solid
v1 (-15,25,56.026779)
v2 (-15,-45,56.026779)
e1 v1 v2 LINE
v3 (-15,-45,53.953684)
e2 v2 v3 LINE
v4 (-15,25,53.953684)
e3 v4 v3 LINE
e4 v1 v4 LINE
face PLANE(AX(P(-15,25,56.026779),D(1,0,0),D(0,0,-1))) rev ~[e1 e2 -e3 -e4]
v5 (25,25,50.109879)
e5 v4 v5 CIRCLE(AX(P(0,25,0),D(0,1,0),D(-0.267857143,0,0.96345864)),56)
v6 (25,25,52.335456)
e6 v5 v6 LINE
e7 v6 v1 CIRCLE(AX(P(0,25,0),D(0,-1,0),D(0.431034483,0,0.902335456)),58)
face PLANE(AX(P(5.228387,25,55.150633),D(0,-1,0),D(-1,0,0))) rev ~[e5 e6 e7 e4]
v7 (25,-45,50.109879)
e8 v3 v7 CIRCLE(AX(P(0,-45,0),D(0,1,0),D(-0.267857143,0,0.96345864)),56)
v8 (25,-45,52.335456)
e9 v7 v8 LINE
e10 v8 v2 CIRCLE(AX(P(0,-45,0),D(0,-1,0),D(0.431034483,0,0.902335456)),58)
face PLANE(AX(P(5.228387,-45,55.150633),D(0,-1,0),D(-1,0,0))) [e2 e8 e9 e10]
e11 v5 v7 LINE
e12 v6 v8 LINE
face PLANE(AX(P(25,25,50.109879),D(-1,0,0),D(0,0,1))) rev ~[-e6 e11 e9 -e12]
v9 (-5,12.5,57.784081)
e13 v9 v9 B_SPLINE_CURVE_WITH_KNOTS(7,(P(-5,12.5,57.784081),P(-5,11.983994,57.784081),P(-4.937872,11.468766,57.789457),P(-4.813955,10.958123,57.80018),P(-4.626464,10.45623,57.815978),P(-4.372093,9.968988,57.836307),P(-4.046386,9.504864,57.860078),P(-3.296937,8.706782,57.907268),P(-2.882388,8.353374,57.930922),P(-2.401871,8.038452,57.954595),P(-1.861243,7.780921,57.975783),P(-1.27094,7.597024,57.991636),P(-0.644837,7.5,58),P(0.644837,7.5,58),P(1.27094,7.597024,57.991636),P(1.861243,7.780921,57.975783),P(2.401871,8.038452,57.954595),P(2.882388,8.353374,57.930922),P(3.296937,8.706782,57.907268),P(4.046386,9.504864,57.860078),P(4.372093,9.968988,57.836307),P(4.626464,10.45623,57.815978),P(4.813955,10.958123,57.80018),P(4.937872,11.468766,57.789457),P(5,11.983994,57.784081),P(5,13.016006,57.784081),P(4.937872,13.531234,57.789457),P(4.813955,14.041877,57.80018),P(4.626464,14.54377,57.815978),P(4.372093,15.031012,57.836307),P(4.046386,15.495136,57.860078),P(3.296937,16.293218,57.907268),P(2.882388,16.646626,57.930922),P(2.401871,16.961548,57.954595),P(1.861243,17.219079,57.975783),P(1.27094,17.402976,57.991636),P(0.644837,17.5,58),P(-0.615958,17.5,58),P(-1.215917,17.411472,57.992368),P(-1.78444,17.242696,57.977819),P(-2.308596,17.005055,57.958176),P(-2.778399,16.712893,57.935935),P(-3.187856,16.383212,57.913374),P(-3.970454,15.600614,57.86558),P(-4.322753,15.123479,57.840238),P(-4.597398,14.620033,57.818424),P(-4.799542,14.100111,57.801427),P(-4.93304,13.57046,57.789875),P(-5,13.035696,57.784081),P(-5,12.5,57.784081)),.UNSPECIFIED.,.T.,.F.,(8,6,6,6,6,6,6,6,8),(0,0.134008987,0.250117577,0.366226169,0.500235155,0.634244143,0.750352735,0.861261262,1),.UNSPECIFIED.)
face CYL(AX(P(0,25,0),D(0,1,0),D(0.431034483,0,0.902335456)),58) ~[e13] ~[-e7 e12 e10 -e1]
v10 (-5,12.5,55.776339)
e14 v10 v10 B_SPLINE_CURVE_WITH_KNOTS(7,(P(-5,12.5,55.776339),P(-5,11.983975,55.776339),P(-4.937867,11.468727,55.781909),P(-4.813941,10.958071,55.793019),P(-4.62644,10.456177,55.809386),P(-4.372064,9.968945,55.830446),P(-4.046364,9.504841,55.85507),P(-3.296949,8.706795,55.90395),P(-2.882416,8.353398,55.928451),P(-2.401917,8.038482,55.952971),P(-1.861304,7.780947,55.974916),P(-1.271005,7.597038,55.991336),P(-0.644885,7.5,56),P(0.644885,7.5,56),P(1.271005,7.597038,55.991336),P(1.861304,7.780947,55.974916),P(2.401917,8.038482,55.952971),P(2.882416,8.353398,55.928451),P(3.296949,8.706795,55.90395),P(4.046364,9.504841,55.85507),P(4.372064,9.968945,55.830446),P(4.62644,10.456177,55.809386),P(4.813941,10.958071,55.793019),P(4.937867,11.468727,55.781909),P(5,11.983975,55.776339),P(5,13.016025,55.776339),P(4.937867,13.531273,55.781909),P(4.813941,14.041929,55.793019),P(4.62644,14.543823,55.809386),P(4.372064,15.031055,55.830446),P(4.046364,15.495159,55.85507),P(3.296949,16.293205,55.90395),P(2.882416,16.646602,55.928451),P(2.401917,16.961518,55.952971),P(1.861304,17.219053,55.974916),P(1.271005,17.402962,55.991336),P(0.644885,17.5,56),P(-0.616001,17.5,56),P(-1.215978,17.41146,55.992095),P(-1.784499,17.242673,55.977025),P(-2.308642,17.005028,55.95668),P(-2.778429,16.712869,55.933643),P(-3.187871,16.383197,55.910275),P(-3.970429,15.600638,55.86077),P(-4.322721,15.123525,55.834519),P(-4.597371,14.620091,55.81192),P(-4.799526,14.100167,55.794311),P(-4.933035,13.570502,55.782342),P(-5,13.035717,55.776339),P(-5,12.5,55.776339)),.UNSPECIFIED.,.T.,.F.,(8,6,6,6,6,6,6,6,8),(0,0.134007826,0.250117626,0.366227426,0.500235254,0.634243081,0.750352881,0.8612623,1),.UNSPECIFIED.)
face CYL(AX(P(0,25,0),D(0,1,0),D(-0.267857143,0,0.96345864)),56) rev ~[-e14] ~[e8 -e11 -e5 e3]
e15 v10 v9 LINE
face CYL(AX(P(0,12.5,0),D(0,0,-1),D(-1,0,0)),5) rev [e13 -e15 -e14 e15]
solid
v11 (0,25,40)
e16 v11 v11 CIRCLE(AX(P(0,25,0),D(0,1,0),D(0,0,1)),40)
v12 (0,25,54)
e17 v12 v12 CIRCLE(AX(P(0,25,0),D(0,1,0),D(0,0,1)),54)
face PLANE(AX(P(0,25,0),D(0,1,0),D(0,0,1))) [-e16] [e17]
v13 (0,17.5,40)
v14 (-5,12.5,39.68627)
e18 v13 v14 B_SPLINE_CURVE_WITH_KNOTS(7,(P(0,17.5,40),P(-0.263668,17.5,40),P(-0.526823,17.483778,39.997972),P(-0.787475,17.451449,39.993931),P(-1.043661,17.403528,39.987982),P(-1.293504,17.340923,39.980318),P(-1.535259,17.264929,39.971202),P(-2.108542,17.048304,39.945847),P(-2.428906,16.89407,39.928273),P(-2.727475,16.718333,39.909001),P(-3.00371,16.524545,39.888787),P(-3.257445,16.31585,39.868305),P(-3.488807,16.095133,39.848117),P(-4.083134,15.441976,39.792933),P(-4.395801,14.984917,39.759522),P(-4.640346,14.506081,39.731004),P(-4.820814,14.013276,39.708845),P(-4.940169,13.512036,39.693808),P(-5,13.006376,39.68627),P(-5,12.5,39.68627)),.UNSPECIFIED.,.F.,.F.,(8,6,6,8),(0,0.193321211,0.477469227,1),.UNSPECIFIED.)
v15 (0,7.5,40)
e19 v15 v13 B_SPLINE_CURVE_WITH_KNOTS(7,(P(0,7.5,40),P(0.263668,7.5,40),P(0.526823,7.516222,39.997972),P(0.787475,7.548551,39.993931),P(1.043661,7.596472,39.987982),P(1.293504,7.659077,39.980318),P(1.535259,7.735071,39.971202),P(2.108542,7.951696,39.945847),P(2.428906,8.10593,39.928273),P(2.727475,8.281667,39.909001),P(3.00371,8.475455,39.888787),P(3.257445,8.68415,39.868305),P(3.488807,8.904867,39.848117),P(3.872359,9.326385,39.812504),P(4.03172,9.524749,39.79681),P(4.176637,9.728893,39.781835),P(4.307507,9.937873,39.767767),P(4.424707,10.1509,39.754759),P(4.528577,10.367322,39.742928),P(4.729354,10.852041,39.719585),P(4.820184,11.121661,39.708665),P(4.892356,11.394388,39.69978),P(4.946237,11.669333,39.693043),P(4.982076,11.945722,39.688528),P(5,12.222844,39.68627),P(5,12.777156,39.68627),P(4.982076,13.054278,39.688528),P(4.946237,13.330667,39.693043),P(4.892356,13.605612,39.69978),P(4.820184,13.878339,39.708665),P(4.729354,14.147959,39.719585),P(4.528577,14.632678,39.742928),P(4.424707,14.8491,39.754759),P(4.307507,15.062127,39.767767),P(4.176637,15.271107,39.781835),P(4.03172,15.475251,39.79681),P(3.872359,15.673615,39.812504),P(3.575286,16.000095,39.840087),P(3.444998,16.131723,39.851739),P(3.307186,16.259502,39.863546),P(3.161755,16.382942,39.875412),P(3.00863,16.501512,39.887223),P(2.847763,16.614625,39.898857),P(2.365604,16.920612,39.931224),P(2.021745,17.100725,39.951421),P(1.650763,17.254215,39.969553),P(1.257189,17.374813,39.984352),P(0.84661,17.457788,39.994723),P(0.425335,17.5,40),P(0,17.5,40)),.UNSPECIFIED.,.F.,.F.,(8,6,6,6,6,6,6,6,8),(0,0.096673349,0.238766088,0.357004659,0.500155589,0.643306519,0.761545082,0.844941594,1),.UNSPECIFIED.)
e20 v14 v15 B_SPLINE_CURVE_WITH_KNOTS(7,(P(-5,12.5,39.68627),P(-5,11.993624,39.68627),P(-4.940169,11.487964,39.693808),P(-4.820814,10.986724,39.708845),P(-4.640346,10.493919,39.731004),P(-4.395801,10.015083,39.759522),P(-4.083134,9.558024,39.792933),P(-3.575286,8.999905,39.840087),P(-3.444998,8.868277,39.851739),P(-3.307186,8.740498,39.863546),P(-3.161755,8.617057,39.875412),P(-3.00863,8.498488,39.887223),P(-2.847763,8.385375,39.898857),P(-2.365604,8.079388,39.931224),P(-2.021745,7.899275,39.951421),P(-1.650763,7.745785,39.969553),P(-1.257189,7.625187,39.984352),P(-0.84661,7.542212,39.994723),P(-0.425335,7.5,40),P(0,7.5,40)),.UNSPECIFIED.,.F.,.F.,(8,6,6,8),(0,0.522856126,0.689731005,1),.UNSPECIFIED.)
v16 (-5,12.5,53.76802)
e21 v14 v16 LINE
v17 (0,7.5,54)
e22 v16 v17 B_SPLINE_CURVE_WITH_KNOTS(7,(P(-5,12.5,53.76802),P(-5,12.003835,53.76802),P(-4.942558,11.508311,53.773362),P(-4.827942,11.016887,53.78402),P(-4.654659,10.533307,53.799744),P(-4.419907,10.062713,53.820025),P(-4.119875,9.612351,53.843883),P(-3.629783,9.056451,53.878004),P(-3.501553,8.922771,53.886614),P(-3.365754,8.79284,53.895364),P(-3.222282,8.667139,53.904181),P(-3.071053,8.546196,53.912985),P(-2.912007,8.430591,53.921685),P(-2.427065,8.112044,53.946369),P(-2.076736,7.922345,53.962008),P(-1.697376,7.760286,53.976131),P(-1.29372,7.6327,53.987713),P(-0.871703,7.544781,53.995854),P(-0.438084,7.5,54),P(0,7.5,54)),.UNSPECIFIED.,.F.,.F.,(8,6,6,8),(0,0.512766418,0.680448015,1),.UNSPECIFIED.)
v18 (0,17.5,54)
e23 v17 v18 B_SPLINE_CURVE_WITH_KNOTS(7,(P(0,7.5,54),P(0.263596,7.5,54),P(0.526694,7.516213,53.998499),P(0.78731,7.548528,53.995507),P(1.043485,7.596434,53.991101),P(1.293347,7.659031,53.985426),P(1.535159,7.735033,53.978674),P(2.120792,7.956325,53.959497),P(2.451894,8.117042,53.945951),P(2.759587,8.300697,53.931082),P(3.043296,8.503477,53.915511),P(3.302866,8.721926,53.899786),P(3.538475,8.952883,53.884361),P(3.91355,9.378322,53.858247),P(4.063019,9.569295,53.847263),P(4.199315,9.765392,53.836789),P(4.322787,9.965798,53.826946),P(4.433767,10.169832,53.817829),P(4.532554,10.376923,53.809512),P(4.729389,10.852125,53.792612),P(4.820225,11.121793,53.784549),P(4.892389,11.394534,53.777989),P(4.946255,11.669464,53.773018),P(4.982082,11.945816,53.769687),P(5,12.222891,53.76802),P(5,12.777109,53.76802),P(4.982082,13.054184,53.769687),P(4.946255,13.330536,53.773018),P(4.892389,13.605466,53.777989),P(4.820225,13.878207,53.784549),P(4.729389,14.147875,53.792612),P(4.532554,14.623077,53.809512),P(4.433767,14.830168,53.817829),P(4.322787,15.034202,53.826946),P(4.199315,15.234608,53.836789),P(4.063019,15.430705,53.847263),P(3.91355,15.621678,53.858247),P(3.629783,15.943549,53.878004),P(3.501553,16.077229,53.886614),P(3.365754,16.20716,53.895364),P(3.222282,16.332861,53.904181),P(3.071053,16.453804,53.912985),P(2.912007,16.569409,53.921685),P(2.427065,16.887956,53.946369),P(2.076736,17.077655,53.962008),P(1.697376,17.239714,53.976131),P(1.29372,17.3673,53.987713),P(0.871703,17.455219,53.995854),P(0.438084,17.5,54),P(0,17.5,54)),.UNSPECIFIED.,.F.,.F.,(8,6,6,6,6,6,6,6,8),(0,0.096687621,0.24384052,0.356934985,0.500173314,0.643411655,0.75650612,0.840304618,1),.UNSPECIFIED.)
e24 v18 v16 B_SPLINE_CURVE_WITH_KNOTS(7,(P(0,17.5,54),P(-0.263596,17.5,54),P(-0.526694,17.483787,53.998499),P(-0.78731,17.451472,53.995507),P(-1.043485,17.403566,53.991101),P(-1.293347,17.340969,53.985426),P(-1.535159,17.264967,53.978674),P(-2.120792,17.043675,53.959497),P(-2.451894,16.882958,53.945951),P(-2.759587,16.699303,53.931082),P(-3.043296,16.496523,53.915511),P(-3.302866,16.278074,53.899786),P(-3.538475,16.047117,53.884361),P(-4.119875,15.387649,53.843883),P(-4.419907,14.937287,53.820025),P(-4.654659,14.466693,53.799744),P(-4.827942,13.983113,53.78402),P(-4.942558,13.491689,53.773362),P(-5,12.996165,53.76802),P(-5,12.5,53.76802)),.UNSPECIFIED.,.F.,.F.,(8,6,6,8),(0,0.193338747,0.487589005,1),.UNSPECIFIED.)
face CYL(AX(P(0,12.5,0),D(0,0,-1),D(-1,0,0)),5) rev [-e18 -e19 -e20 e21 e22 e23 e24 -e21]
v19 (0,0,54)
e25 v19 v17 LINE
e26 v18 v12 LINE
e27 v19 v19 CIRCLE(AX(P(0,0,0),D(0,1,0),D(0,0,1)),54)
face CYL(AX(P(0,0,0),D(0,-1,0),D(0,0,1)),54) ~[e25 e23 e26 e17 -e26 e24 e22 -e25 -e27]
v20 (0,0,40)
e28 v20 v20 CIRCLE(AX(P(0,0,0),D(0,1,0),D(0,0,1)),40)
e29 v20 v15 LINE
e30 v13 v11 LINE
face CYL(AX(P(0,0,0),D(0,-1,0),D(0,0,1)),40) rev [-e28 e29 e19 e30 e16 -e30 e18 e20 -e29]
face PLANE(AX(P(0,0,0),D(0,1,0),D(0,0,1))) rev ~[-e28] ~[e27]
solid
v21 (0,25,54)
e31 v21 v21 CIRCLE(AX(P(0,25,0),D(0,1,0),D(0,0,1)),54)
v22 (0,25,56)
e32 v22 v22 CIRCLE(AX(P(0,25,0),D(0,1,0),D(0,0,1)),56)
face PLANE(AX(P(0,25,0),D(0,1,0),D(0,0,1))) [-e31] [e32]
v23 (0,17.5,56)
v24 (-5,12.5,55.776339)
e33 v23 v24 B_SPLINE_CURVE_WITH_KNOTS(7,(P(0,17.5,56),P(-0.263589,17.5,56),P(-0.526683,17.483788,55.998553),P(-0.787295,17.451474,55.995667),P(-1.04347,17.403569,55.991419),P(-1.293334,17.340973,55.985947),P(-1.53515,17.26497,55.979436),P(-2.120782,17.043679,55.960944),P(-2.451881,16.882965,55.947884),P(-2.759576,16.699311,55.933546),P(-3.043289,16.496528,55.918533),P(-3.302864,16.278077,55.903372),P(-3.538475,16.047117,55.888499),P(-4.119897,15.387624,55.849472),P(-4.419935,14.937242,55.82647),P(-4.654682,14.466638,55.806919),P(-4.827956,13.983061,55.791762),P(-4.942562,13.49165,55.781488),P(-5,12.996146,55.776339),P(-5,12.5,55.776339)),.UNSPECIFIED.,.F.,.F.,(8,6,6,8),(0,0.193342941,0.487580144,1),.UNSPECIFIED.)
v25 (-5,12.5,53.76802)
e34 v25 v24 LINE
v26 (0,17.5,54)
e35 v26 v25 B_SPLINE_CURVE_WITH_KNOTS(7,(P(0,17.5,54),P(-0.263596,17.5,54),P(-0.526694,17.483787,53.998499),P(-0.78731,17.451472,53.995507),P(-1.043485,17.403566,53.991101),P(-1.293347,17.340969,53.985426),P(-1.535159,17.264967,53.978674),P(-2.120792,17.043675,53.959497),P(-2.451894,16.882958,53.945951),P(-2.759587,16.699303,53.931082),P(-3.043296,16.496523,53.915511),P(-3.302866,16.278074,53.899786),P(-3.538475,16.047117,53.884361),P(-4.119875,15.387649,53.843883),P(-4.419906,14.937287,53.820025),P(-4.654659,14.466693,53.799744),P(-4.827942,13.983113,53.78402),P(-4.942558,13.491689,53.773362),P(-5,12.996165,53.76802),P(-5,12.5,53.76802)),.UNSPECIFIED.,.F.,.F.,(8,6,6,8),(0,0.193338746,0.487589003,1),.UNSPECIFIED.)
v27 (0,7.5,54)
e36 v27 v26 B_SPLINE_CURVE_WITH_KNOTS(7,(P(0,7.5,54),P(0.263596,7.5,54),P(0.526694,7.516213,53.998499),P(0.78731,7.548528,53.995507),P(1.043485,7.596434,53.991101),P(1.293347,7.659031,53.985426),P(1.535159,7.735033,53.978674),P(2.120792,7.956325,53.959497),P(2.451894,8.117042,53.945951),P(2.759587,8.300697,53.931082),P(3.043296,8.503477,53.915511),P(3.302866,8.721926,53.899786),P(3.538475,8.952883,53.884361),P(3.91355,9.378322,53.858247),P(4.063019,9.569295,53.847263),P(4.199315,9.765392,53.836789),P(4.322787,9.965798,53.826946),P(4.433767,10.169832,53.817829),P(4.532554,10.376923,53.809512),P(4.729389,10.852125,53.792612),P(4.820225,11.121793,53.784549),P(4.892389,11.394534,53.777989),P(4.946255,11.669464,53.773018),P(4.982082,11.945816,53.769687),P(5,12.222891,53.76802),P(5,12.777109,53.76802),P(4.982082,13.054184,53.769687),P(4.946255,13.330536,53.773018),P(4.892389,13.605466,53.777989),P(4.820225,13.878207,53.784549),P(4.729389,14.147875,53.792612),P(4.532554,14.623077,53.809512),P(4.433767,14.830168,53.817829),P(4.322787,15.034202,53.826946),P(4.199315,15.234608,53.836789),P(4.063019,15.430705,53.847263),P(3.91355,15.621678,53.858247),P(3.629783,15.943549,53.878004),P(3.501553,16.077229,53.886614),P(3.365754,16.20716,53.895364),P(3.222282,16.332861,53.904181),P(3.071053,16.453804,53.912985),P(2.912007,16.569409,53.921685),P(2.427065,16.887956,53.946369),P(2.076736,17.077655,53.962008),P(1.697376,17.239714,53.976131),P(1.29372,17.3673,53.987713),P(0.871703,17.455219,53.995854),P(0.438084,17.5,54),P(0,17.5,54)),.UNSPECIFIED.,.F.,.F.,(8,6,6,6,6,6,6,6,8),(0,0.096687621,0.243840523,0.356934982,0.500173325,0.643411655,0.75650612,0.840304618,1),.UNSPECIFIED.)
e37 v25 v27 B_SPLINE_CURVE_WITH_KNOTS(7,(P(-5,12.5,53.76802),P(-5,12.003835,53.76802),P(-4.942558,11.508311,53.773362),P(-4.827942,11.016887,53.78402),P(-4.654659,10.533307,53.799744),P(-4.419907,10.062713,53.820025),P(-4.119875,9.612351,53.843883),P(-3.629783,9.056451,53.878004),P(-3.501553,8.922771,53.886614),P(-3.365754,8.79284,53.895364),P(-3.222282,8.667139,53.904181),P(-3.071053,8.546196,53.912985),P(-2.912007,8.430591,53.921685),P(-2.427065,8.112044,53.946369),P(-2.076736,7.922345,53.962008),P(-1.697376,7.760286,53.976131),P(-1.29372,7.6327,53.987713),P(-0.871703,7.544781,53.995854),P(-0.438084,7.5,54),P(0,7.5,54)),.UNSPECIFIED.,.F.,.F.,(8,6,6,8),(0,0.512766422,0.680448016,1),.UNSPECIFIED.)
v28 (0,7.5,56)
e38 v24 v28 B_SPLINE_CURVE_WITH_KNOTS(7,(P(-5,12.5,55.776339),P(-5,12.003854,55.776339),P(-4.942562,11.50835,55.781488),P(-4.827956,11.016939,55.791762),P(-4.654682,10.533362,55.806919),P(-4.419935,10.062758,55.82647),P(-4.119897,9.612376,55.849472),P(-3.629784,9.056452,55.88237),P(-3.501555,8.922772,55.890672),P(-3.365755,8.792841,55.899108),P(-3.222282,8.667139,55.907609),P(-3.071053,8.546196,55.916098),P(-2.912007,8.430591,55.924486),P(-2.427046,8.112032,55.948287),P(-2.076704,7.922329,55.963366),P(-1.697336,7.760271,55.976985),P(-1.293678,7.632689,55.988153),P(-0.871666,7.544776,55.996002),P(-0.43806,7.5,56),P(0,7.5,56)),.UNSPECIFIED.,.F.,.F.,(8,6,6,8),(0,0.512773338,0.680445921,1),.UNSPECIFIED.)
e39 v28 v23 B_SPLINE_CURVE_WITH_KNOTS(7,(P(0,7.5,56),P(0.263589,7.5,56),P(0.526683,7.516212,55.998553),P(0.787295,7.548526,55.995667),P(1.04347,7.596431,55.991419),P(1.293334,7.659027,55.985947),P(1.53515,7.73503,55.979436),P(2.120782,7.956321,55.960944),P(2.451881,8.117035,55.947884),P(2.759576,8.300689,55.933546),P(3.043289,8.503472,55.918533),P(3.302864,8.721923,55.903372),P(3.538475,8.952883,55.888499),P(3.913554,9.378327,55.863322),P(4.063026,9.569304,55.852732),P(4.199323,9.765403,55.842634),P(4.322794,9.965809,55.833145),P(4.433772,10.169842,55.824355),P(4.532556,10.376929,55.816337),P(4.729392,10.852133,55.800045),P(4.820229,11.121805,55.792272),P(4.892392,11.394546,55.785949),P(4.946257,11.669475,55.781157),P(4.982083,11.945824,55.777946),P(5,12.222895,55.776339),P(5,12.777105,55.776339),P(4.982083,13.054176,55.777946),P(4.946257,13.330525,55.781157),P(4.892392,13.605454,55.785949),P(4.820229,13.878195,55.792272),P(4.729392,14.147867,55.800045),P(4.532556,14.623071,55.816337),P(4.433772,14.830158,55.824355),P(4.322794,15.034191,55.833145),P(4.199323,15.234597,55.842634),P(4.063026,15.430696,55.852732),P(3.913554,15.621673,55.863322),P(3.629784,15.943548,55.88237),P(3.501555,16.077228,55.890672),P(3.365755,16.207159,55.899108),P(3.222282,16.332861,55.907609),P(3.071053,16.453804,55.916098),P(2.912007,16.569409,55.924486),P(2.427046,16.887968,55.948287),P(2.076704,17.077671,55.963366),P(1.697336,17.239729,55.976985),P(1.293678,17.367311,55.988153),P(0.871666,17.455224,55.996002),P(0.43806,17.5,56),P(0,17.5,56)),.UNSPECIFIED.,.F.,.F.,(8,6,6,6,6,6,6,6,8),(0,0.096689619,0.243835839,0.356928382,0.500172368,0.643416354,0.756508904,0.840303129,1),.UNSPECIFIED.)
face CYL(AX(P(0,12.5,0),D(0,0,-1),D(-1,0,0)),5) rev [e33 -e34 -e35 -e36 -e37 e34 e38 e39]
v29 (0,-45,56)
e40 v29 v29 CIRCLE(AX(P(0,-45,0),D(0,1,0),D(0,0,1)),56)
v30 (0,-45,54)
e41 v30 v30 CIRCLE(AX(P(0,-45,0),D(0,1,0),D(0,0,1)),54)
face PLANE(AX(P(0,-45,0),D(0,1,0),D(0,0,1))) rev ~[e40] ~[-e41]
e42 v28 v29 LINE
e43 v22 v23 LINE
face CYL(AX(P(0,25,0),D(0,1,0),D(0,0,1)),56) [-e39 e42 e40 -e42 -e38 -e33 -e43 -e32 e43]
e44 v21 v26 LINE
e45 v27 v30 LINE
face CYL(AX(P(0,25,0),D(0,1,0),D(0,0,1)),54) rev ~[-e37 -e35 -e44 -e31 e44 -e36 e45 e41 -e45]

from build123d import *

# Parameters (mm, degrees)
SKETCH_1_R          = 54
SKETCH_1_R_2        = 40
EXTRUDE_1_DEPTH     = 25
SKETCH_2_R          = 56
SKETCH_2_R_2        = 54
EXTRUDE_2_DEPTH     = 70
EXTRUDE_3_DEPTH     = 70
SKETCH_3_R          = 5
CUT_EXTRUDE_1_DEPTH = 93.330926563


with BuildPart() as part:
    # 草图1 → 凸台-拉伸1 (new body)
    with BuildSketch(Plane(origin=(0, 0, 0), x_dir=(1, 0, 0), z_dir=(0, 1, 0))):
        with Locations(Location((0, 0, 0), (0, 0, 270))):
            Circle(SKETCH_1_R)
        with Locations(Location((0, 0, 0), (0, 0, 270))):
            Circle(SKETCH_1_R_2, mode=Mode.SUBTRACT)
    extrude(amount=EXTRUDE_1_DEPTH)


with BuildPart() as body_2:
    # 草图2 → 凸台-拉伸2 (new body)
    with BuildSketch(Plane(origin=(0, 25, 0), x_dir=(1, 0, 0), z_dir=(0, 1, 0))):
        with Locations(Location((0, 0, 0), (0, 0, 270))):
            Circle(SKETCH_2_R)
        with Locations(Location((0, 0, 0), (0, 0, 270))):
            Circle(SKETCH_2_R_2, mode=Mode.SUBTRACT)
    extrude(amount=-EXTRUDE_2_DEPTH)


with BuildPart() as body_3:
    # 草图4 → 凸台-拉伸3 (new body)
    with BuildSketch(Plane(origin=(0, 25, 0), x_dir=(1, 0, 0), z_dir=(0, 1, 0))):
        with BuildLine():
            Line((25, -50.109879265), (25, -52.335456433))
            ThreePointArc((25, -52.335456433), (5.329771679, -57.754597513), (-15, -56.026779311))
            Line((-15, -56.026779311), (-15, -53.953683841))
            ThreePointArc((-15, -53.953683841), (5.356650857, -55.743217449), (25, -50.109879265))
        make_face()
    extrude(amount=-EXTRUDE_3_DEPTH)


with BuildPart() as cut_extrude_1_tool:
    # 草图3 → 切除-拉伸1 (new, through all)
    with BuildSketch(Plane.XY):
        with Locations(Location((0, 12.5, 0), (0, 0, 180))):
            Circle(SKETCH_3_R)
    extrude(amount=CUT_EXTRUDE_1_DEPTH)


with BuildPart() as part_1:
    add(part.part)

    # 切除-拉伸1: cut by cut_extrude_1_tool
    add(cut_extrude_1_tool.part, mode=Mode.SUBTRACT)


with BuildPart() as body_2_1:
    add(body_2.part)

    # 切除-拉伸1: cut by cut_extrude_1_tool
    add(cut_extrude_1_tool.part, mode=Mode.SUBTRACT)


with BuildPart() as body_3_1:
    add(body_3.part)

    # 切除-拉伸1: cut by cut_extrude_1_tool
    add(cut_extrude_1_tool.part, mode=Mode.SUBTRACT)


solid = Compound([part_1.part, body_2_1.part, body_3_1.part])
